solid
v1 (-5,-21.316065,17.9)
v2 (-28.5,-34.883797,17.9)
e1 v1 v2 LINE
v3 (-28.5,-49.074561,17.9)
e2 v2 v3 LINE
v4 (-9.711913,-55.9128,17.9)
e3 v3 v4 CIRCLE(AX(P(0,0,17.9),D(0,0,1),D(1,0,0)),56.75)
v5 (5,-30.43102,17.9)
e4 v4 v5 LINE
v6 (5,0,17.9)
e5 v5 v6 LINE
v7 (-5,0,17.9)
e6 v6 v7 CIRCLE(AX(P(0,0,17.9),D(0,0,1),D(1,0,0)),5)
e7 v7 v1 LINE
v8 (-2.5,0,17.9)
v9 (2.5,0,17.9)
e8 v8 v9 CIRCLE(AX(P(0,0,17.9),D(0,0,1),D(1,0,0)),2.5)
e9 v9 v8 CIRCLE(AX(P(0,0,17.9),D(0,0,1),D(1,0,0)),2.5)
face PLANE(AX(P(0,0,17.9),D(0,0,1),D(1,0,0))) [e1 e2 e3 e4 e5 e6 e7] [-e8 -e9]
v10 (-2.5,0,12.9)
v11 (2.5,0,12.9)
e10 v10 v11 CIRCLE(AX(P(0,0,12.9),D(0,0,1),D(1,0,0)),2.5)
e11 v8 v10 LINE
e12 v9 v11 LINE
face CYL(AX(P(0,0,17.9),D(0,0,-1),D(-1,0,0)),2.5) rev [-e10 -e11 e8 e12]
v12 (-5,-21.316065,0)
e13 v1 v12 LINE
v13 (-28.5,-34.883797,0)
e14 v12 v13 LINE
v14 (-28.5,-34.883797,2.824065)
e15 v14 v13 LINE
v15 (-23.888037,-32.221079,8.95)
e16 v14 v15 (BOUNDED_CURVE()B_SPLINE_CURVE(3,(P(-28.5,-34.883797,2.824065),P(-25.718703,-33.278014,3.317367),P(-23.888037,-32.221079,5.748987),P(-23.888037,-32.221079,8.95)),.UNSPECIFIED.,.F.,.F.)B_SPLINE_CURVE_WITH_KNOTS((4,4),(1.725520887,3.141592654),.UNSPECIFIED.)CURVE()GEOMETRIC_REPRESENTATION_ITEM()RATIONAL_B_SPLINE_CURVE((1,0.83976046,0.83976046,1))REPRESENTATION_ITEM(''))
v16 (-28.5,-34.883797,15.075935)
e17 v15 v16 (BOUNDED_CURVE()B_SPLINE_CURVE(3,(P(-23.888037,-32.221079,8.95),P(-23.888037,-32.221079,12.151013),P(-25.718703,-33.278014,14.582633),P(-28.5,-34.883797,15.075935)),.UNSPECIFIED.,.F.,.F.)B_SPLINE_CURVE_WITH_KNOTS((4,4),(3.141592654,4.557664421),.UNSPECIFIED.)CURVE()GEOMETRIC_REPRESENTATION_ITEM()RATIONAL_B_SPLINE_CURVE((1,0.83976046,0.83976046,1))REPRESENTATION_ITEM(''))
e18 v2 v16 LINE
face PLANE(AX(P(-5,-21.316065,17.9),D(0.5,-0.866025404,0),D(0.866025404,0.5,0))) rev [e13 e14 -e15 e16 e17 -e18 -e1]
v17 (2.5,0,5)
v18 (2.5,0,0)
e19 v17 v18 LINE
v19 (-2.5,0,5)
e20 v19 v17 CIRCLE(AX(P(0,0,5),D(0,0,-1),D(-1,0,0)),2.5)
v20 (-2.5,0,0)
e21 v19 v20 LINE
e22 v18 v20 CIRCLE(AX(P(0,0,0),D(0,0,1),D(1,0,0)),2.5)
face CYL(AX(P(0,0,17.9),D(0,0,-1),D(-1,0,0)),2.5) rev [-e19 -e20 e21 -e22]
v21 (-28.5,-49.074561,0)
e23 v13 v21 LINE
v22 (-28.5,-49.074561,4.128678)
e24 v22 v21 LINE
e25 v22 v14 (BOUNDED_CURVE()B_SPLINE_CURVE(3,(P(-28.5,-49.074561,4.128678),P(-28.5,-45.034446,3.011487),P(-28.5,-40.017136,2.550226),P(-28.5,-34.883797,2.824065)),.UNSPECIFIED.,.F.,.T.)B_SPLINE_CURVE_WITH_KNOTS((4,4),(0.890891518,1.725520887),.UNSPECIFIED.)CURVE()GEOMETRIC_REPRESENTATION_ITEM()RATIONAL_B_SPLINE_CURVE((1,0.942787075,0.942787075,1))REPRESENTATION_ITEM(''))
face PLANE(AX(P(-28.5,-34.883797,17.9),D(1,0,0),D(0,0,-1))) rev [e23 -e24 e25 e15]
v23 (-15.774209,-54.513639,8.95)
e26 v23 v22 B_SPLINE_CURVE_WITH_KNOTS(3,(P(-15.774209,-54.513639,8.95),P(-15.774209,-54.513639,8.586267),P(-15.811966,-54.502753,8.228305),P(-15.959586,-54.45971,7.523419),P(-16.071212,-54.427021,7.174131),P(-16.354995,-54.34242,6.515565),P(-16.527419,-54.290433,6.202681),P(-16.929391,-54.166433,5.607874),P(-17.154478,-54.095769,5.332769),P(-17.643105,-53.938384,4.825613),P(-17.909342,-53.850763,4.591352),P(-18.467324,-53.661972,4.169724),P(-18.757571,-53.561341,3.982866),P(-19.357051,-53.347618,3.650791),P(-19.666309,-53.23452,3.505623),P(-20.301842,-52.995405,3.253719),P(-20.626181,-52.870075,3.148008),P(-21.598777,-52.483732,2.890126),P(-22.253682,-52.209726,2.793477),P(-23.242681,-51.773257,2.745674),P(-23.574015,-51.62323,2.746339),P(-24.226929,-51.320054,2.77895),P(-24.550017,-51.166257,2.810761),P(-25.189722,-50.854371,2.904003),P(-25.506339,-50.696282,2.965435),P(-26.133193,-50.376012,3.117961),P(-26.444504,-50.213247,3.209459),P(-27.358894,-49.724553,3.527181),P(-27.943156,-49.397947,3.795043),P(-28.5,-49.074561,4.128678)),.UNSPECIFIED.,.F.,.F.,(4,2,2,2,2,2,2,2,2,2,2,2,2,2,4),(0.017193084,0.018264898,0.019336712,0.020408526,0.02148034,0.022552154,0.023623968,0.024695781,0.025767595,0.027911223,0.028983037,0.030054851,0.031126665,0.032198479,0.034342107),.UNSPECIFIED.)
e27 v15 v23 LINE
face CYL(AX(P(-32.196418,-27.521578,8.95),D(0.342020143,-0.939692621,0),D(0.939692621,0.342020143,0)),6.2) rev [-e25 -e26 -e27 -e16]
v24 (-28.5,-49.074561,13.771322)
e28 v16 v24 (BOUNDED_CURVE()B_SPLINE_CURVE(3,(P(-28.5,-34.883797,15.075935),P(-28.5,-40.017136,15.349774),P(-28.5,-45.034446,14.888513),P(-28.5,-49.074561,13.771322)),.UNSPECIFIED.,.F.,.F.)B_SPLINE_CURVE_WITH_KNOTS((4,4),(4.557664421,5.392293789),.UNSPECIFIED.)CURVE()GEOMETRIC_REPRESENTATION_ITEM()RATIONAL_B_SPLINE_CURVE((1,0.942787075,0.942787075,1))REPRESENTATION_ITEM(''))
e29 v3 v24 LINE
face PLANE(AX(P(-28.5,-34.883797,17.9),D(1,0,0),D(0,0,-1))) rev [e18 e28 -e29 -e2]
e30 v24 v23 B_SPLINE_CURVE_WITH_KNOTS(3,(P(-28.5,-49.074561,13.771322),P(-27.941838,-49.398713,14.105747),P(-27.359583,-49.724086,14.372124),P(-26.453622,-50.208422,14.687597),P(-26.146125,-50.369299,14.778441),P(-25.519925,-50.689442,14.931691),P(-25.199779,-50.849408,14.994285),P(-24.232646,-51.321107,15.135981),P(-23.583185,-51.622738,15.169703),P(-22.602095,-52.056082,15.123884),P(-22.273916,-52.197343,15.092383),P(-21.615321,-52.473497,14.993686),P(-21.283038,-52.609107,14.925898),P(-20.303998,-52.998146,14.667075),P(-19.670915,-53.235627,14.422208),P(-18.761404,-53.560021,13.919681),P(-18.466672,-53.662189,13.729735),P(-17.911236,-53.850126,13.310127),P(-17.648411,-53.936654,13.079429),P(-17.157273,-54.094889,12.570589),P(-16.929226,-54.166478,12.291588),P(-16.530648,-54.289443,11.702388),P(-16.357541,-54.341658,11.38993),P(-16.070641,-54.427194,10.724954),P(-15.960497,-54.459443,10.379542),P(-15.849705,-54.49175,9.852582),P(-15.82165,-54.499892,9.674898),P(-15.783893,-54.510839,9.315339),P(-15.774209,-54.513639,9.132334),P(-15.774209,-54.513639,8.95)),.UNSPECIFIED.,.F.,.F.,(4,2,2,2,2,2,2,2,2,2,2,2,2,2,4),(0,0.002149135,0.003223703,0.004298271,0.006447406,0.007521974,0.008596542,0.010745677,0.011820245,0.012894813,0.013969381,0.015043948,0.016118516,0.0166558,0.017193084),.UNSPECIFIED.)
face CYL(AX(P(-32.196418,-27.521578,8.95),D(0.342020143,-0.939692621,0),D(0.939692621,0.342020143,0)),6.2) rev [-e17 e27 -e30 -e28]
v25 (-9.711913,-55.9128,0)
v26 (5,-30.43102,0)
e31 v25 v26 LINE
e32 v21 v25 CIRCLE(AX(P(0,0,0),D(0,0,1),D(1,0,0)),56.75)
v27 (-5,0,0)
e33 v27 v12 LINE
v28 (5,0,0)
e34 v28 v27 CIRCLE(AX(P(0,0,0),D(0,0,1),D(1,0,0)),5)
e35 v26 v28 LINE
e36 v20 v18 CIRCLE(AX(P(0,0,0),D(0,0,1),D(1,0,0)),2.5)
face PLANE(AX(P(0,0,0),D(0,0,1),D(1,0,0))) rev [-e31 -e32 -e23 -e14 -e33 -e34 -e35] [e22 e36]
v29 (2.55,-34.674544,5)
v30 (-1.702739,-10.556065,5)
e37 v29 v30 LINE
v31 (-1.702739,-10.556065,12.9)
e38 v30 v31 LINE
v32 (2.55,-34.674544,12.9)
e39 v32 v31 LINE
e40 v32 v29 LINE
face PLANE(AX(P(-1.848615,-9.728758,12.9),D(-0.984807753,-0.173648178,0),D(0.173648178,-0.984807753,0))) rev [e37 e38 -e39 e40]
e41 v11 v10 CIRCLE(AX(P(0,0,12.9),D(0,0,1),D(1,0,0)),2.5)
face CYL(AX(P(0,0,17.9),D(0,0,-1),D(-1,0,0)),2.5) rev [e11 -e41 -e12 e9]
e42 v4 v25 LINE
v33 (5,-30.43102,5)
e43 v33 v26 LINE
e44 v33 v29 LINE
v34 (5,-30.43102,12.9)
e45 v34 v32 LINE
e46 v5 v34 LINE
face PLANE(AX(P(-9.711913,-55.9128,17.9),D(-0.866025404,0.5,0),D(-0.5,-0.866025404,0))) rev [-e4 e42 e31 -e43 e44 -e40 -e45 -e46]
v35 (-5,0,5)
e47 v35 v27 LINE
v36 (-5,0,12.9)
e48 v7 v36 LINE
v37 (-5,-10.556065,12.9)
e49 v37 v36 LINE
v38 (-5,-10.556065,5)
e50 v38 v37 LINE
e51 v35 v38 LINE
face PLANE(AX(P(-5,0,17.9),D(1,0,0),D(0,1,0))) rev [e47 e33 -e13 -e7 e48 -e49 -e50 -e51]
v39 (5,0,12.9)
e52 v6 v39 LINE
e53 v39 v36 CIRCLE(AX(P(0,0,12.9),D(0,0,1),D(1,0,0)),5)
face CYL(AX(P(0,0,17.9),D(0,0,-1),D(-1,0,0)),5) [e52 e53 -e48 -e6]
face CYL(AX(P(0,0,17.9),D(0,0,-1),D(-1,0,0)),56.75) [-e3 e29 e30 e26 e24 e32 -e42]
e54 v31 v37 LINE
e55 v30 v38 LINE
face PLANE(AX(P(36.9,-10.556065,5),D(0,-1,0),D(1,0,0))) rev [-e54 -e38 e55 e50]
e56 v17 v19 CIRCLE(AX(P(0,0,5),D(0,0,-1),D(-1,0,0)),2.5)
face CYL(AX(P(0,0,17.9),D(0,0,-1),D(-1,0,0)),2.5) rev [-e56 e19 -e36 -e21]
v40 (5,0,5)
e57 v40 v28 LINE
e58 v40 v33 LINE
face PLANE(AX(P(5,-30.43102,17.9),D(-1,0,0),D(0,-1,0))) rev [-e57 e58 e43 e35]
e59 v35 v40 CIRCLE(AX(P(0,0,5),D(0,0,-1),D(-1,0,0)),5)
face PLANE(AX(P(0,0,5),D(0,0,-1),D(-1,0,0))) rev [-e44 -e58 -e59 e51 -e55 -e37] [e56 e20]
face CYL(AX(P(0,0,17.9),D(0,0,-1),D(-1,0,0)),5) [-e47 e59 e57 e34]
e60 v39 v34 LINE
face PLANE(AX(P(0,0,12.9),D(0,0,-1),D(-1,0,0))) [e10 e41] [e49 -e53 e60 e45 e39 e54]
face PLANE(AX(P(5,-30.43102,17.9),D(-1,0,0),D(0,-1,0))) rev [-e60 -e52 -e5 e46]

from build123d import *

# Parameters (mm, degrees)
SKETCH2_R           = 2.5
BOSS_EXTRUDE1_DEPTH = 17.9
CUT_EXTRUDE1_DEPTH  = 3.95
SKETCH4_W           = 7.9
SKETCH4_H           = 17.88597718
CUT_EXTRUDE2_DEPTH  = 41.9
SKETCH5_R           = 6.2
CUT_EXTRUDE3_DEPTH  = 41.9


with BuildPart() as part:
    # Sketch2 → Boss-Extrude1 (new body)
    with BuildSketch(Plane.XY):
        with BuildLine():
            Line((5, -30.431019852), (5, 0))
            ThreePointArc((5, 0), (0, 5), (-5, 0))
            Line((-5, 0), (-5, -21.316065276))
            Line((-5, -21.316065276), (-28.5, -34.883796602))
            Line((-28.5, -34.883796602), (-28.5, -49.07456062))
            ThreePointArc((-28.5, -49.07456062), (-19.40948098, -53.327615248), (-9.711912859, -55.9128004))
            Line((-9.711912859, -55.9128004), (5, -30.431019852))
        make_face()
        with Locations(Location((0, 0, 0), (0, 0, 180))):
            Circle(SKETCH2_R, mode=Mode.SUBTRACT)
    extrude(amount=BOSS_EXTRUDE1_DEPTH)

    # Sketch3 → Cut-Extrude1 (cut, symmetric)
    with BuildSketch(Plane(origin=(0, 0, 8.95), x_dir=(-1, 0, 0), z_dir=(0, 0, -1))):
        Polygon((1.84861519, -9.72875797), (-2.55, -34.674544331), (-5, -30.431019852), (-5, -8.521162332), align=None)
    extrude(amount=CUT_EXTRUDE1_DEPTH, both=True, mode=Mode.SUBTRACT)

    # Sketch4 → Cut-Extrude2 (cut)
    with BuildSketch(Plane.ZY.offset(5)):
        with Locations((8.95, -1.613076686)):
            Rectangle(SKETCH4_W, SKETCH4_H)
    extrude(amount=-CUT_EXTRUDE2_DEPTH, mode=Mode.SUBTRACT)

    # Sketch5 → Cut-Extrude3 (cut)
    with BuildSketch(Plane(origin=(19.409643134, -53.32755623, 0), x_dir=(0, 0, -1), z_dir=(0.34202014332566744, -0.9396926207859089, 0))):
        with Locations((-8.95, -39.667670129)):
            Circle(SKETCH5_R)
    extrude(amount=-CUT_EXTRUDE3_DEPTH, mode=Mode.SUBTRACT)


solid = part.part
